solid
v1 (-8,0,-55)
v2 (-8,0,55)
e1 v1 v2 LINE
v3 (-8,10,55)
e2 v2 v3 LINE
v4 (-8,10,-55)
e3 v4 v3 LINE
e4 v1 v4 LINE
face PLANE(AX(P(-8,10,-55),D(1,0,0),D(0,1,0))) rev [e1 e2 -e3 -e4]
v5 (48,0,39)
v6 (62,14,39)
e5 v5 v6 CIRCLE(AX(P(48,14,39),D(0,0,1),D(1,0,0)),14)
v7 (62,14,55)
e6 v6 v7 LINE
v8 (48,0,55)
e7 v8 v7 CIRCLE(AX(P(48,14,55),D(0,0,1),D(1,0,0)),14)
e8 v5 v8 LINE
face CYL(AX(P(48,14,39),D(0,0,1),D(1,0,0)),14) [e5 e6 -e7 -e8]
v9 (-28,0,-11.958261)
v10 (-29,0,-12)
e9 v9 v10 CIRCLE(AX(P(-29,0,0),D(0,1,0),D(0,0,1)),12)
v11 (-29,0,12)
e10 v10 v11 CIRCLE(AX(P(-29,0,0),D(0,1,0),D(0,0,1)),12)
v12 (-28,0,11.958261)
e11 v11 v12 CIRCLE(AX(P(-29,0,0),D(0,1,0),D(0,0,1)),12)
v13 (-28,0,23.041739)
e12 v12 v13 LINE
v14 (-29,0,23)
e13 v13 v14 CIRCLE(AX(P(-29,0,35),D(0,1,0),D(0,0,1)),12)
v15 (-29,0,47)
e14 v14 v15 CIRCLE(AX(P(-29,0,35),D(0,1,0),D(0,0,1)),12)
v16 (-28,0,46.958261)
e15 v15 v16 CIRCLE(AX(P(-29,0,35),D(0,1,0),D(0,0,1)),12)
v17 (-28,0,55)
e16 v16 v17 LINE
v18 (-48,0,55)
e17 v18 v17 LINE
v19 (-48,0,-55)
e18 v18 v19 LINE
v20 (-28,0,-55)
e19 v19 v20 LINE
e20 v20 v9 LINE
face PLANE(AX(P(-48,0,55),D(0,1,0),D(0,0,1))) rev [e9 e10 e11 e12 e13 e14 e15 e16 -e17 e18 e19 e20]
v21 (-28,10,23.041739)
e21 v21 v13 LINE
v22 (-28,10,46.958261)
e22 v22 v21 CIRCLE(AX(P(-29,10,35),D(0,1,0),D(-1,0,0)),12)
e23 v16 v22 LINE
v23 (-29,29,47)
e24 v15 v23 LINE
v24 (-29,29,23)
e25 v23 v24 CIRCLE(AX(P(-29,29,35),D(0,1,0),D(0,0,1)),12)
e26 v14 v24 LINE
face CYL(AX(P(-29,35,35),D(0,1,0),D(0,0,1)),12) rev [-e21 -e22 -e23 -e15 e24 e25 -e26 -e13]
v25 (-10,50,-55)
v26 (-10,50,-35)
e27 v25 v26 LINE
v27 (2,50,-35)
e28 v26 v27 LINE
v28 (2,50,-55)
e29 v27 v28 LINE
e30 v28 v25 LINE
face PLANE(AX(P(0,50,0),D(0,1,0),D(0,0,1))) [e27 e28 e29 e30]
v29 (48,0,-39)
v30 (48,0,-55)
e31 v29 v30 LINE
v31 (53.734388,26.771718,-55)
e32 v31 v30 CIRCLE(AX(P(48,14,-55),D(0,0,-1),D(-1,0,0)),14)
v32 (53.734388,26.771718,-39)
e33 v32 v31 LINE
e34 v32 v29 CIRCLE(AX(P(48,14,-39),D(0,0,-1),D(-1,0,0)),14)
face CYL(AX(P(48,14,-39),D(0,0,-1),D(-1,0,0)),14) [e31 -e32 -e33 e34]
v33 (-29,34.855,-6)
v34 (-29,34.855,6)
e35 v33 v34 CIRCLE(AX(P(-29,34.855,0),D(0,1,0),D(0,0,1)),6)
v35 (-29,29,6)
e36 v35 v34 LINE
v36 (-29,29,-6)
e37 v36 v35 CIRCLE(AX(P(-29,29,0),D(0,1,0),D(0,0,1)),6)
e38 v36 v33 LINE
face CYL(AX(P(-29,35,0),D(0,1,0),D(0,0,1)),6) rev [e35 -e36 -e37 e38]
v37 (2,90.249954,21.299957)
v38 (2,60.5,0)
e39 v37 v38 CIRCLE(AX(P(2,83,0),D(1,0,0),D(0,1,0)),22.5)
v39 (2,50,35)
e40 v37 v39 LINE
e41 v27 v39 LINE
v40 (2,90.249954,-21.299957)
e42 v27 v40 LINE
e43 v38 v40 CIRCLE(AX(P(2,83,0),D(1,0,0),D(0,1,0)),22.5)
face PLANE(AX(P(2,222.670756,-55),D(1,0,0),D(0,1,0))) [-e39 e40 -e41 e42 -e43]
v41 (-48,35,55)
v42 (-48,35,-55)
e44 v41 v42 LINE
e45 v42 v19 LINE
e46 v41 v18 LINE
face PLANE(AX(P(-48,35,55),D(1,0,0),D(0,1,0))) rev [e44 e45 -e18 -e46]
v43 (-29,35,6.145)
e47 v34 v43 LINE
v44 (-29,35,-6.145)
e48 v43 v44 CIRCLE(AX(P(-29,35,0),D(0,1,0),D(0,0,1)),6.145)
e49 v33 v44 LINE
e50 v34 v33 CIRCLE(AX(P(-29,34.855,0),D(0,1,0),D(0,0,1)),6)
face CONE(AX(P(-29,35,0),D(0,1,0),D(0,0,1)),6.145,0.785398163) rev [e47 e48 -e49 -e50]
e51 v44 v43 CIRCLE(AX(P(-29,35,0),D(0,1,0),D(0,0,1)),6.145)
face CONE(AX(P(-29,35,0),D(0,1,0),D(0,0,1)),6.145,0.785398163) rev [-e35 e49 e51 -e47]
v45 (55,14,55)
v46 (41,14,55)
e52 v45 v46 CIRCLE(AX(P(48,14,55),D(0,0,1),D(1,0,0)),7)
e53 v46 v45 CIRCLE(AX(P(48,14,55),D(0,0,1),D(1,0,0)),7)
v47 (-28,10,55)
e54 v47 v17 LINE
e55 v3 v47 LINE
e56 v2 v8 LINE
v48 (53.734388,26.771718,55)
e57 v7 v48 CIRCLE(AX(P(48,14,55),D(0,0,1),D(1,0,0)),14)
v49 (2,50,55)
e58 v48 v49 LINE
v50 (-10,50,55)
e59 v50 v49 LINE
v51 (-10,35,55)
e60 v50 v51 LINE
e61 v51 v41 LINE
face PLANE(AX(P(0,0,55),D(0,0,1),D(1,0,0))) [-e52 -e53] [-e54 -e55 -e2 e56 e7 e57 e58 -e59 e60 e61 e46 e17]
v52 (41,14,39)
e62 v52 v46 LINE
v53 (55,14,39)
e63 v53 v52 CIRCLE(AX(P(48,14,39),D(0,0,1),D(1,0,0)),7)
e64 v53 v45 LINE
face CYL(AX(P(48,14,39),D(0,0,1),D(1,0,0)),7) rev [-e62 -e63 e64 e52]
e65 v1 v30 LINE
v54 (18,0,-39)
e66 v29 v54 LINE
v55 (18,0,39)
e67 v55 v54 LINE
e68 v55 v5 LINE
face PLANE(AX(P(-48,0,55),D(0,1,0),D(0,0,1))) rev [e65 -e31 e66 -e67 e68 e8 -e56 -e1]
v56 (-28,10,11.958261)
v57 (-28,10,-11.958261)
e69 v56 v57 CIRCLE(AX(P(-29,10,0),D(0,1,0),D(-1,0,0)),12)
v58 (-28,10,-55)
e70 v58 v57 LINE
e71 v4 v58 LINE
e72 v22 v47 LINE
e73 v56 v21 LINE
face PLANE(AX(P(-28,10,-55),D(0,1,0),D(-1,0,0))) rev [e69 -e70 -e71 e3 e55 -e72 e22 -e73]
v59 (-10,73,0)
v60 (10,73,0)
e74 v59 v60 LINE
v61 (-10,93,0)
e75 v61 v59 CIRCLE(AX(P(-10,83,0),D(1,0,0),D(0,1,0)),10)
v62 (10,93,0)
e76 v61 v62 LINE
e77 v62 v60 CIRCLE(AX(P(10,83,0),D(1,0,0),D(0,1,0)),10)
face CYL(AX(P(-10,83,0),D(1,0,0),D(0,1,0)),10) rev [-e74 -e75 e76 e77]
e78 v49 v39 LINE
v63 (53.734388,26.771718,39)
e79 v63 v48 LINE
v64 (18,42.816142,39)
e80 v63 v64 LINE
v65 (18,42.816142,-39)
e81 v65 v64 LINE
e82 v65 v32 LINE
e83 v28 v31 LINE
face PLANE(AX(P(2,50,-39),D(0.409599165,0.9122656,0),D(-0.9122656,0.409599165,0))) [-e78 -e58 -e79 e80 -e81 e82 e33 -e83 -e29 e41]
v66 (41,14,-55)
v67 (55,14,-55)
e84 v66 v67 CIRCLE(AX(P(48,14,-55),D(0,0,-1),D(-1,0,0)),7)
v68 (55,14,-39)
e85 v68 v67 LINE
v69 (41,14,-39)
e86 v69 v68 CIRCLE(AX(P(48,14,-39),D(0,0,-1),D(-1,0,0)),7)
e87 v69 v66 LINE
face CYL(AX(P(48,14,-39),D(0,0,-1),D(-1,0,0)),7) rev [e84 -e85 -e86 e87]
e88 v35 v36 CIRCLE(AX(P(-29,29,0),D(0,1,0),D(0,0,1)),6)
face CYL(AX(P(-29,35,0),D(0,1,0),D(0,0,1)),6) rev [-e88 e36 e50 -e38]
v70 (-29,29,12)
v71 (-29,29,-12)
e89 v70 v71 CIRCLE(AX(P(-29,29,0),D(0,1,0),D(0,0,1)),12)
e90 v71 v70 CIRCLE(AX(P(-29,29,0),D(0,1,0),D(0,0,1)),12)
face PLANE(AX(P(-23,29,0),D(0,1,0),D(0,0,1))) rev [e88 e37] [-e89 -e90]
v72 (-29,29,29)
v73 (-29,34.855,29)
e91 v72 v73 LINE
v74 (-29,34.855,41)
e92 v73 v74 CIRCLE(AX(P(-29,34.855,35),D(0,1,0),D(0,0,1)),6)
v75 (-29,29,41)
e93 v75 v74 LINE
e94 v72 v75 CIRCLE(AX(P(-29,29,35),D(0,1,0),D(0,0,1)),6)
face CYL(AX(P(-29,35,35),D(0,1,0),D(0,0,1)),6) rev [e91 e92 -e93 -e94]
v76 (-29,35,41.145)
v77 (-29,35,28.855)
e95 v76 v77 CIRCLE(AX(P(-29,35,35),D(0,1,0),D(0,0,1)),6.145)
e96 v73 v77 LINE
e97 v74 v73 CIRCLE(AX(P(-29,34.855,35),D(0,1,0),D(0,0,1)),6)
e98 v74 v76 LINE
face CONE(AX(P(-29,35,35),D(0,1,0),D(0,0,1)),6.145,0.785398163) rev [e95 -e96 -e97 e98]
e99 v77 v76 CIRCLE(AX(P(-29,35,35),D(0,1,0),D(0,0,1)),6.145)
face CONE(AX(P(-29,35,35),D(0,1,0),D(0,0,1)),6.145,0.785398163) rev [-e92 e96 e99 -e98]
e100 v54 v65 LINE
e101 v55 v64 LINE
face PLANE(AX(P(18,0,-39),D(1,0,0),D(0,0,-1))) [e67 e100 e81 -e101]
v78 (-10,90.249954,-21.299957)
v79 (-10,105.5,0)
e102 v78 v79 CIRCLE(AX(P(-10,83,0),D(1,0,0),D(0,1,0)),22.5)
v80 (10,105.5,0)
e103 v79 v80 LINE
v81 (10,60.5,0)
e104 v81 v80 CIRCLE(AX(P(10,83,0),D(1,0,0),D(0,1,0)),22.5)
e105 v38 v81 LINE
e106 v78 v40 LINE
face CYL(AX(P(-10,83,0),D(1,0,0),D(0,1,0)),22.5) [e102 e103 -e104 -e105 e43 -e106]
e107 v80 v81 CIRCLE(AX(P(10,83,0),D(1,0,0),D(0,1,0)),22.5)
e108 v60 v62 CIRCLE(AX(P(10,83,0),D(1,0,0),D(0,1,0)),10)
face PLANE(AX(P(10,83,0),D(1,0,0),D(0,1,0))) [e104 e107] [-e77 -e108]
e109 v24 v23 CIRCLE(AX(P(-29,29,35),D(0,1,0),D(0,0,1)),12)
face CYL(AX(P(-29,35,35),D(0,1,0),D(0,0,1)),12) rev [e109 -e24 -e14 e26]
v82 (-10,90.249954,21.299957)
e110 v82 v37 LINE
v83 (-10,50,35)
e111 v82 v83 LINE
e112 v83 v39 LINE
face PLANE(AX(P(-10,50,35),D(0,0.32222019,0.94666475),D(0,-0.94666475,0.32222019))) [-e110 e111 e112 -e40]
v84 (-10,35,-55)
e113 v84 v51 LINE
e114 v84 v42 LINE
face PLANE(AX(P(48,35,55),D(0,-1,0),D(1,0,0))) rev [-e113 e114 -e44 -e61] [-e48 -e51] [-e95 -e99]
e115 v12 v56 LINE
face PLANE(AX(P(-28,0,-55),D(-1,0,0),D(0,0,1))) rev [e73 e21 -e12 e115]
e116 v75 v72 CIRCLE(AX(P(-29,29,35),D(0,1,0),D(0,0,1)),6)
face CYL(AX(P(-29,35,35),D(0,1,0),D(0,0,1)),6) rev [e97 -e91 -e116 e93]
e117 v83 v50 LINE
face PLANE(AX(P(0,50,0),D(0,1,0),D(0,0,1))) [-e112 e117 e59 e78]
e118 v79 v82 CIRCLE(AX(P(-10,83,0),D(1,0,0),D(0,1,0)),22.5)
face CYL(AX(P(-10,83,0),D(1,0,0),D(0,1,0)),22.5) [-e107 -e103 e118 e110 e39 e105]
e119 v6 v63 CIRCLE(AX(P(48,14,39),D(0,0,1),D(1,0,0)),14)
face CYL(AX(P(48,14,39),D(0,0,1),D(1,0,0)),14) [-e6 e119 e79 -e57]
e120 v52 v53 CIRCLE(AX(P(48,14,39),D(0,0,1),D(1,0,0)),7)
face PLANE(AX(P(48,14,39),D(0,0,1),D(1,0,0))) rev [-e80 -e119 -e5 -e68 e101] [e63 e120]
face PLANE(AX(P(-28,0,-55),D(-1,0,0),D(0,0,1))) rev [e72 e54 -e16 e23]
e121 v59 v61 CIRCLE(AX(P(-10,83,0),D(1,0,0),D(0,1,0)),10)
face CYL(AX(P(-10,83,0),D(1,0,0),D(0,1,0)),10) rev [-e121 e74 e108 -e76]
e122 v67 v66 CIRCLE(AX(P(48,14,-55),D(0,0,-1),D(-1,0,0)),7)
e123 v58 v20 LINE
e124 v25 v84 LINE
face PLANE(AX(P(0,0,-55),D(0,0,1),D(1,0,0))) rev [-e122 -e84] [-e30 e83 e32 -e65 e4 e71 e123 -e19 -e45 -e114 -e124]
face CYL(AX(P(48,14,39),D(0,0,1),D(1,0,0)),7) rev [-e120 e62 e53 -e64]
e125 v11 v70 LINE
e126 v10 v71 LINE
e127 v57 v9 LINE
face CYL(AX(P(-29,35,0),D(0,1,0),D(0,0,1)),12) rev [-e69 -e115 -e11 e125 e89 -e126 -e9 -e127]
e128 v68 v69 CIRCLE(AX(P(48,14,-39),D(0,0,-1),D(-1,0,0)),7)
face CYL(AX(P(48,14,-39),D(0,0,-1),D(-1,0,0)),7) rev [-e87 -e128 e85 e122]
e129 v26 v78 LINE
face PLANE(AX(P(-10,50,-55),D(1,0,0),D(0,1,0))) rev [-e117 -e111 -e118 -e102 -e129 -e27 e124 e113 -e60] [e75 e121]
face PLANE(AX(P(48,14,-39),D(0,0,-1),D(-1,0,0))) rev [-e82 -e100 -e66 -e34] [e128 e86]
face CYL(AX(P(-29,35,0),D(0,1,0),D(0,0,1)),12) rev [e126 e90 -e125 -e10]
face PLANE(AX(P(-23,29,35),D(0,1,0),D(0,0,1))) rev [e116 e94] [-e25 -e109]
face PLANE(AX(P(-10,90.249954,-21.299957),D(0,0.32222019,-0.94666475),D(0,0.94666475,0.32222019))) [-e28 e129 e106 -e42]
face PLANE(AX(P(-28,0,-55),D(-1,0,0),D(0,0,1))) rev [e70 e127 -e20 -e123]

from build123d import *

# Parameters (mm, degrees)
BASE_BLOCK_PROFILE_SKETCH_W       = 96
BASE_BLOCK_PROFILE_SKETCH_H       = 35
BASE_BLOCK_DEPTH                  = 55
BASE_STEP_RECESS_DEPTH            = 81.956778592
BASE_STEP_RECESS_DEPTH_BACK       = 35
BASE_GROOVE_20X20_SKETCH_W        = 20
BASE_GROOVE_20X20_SKETCH_H        = 10
BASE_GROOVE_20X20_DEPTH           = 110
UPRIGHT_PAD_SKETCH_W              = 12
UPRIGHT_PAD_SKETCH_H              = 110
UPRIGHT_PAD_DEPTH                 = 15
LUG_PLATE_DEPTH                   = 12
LUG_START                         = 8
LUG_HUB_SKETCH_R                  = 22.5
LUG_HUB_DEPTH                     = 8
LUG_BORE_20_SKETCH_R              = 10
LUG_BORE_20_DEPTH                 = 20
SIDE_ARM_A_DEPTH                  = 16
SIDE_START                        = -16
SIDE_ARM_B_DEPTH                  = 16
ARM_B_EYE_HOLE_14_SKETCH_R        = 7
ARM_B_EYE_HOLE_14_DEPTH           = 16
ARM_START                         = -16
ARM_A_EYE_HOLE_14_SKETCH_R        = 7
ARM_A_EYE_HOLE_14_DEPTH           = 16
CROSS_WEB_SKETCH_W                = 16
CROSS_WEB_SKETCH_H                = 78
CROSS_WEB_DEPTH                   = 50
TRIANGULAR_RELIEF_CUT_REACH       = 156.306
COUNTERBORED_BOLT_HOLE_AT_2_COUNT = 2
COUNTERBORED_BOLT_HOLE_AT_2_PITCH = 35


with BuildPart() as part:
    # Base Block Profile Sketch → Base Block (new, symmetric)
    with BuildSketch(Plane.XY):
        with Locations((0, 17.5)):
            Rectangle(BASE_BLOCK_PROFILE_SKETCH_W, BASE_BLOCK_PROFILE_SKETCH_H)
    extrude(amount=BASE_BLOCK_DEPTH, both=True)

    # Base Step Recess Sketch → Base Step Recess (cut, two sides: drawn at the far end of the back side and taken through both)
    with BuildSketch(Plane(origin=(0, 35, 0), x_dir=(1, 0, 0), z_dir=(0, 1, 0)).offset(-BASE_STEP_RECESS_DEPTH_BACK)):
        Polygon((48, 55), (47.003525264, 55), (2, 55), (2, -55), (48, -55), align=None)
    extrude(amount=BASE_STEP_RECESS_DEPTH + BASE_STEP_RECESS_DEPTH_BACK, mode=Mode.SUBTRACT)

    # Base Groove 20x20 Sketch → Base Groove 20x20 (cut)
    with BuildSketch(Plane.XY.offset(55)):
        with Locations((-18, 5)):
            Rectangle(BASE_GROOVE_20X20_SKETCH_W, BASE_GROOVE_20X20_SKETCH_H)
    extrude(amount=-BASE_GROOVE_20X20_DEPTH, mode=Mode.SUBTRACT)

    # Upright Pad Sketch → Upright Pad (add)
    with BuildSketch(Plane(origin=(0, 35, 0), x_dir=(1, 0, 0), z_dir=(0, 1, 0))):
        with Locations((-4, 0)):
            Rectangle(UPRIGHT_PAD_SKETCH_W, UPRIGHT_PAD_SKETCH_H)
    extrude(amount=UPRIGHT_PAD_DEPTH)

    # Lug Plate Sketch → Lug Plate (add)
    with BuildSketch(Plane(origin=(2, 0, 0), x_dir=(0, 0, -1), z_dir=(1, 0, 0))):
        with BuildLine():
            Line((-35, 50), (-21.299956881, 90.249954267))
            ThreePointArc((-21.299956881, 90.249954267), (0, 105.5), (21.299956881, 90.249954267))
            Line((21.299956881, 90.249954267), (35, 50))
            Line((35, 50), (0, 50))
            Line((0, 50), (-35, 50))
        make_face()
    extrude(amount=-LUG_PLATE_DEPTH)

    # Lug Hub Sketch → Lug Hub (add)
    with BuildSketch(Plane(origin=(2, 0, 0), x_dir=(0, 0, -1), z_dir=(1, 0, 0)).offset(LUG_START)):
        with Locations(Location((0, 83, 0), (0, 0, 90))):
            Circle(LUG_HUB_SKETCH_R)
    extrude(amount=-LUG_HUB_DEPTH)

    # Lug Bore Ø20 Sketch → Lug Bore Ø20 (cut)
    with BuildSketch(Plane(origin=(10, 0, 0), x_dir=(0, 0, -1), z_dir=(1, 0, 0))):
        with Locations(Location((0, 83, 0), (0, 0, 90))):
            Circle(LUG_BORE_20_SKETCH_R)
    extrude(amount=-LUG_BORE_20_DEPTH, mode=Mode.SUBTRACT)

    # Side Arm A Sketch → Side Arm A (add)
    with BuildSketch(Plane(origin=(0, 0, -55), x_dir=(-1, 0, 0), z_dir=(0, 0, -1))):
        with BuildLine():
            Line((8, 0), (-48, 0))
            ThreePointArc((-48, 0), (-61.689486066, 11.067770261), (-53.734388308, 26.771718394))
            Line((-53.734388308, 26.771718394), (-2, 50))
            Line((-2, 50), (10, 50))
            Line((10, 50), (10, 35))
            Line((10, 35), (10, 10))
            Line((10, 10), (8, 10))
            Line((8, 10), (8, 0))
        make_face()
    extrude(amount=-SIDE_ARM_A_DEPTH)

    # Side Arm B Sketch → Side Arm B (add)
    with BuildSketch(Plane.XY.offset(55).offset(SIDE_START)):
        with BuildLine():
            Line((-8, 0), (48, 0))
            ThreePointArc((48, 0), (61.689486066, 11.067770261), (53.734388308, 26.771718394))
            Line((53.734388308, 26.771718394), (2, 50))
            Line((2, 50), (-10, 50))
            Line((-10, 50), (-10, 35))
            Line((-10, 35), (-13.136025353, 35))
            Line((-13.136025353, 35), (-13.136025353, 10))
            Line((-13.136025353, 10), (-8, 10))
            Line((-8, 10), (-8, 0))
        make_face()
    extrude(amount=SIDE_ARM_B_DEPTH)

    # Arm B Eye Hole Ø14 Sketch → Arm B Eye Hole Ø14 (cut)
    with BuildSketch(Plane.XY.offset(55)):
        with Locations((48, 14)):
            Circle(ARM_B_EYE_HOLE_14_SKETCH_R)
    extrude(amount=-ARM_B_EYE_HOLE_14_DEPTH, mode=Mode.SUBTRACT)

    # Arm A Eye Hole Ø14 Sketch → Arm A Eye Hole Ø14 (cut)
    with BuildSketch(Plane(origin=(0, 0, -55), x_dir=(-1, 0, 0), z_dir=(0, 0, -1)).offset(ARM_START)):
        with Locations(Location((-48, 14, 0), (0, 0, 180))):
            Circle(ARM_A_EYE_HOLE_14_SKETCH_R)
    extrude(amount=ARM_A_EYE_HOLE_14_DEPTH, mode=Mode.SUBTRACT)

    # Cross Web Sketch → Cross Web (add)
    with BuildSketch(Plane(origin=(0, 50, 0), x_dir=(1, 0, 0), z_dir=(0, 1, 0))):
        with Locations((10, 0)):
            Rectangle(CROSS_WEB_SKETCH_W, CROSS_WEB_SKETCH_H)
    extrude(amount=-CROSS_WEB_DEPTH)

    # Triangular Relief Sketch → Triangular Relief Cut (cut, up to next)
    with BuildSketch(Plane.XY.offset(39), mode=Mode.PRIVATE) as triangular_relief_cut_sk1:
        Polygon((2, 50), (18, 42.816141877), (18, 50), align=None)
    triangular_relief_cut_tool1 = extrude(triangular_relief_cut_sk1.sketch, amount=-TRIANGULAR_RELIEF_CUT_REACH, mode=Mode.PRIVATE) & part.part
    add(triangular_relief_cut_tool1.solids().sort_by_distance((12.666667, 47.605381, 39))[0], mode=Mode.SUBTRACT)

    # Sketch42 → Counterbored Bolt Hole (revolve, cut)
    with BuildSketch(Plane(origin=(-29, 35, 35), x_dir=(0, 0, 1), z_dir=(1, 0, 0))):
        Polygon((0, 0), (0, 35), (12, 35), (12, 6), (6, 6), (6, 0.145), (6.145, 0), align=None)
    counterbored_bolt_hole = revolve(axis=Axis((-29, 41.35, 35), (0, -1, 0)), mode=Mode.SUBTRACT)

    # Counterbored Bolt Hole at 2: Counterbored Bolt Hole ×2
    with Locations(*[(0, 0, -i * COUNTERBORED_BOLT_HOLE_AT_2_PITCH) for i in range(1, COUNTERBORED_BOLT_HOLE_AT_2_COUNT)]):
        add(counterbored_bolt_hole, mode=Mode.SUBTRACT)


solid = part.part
